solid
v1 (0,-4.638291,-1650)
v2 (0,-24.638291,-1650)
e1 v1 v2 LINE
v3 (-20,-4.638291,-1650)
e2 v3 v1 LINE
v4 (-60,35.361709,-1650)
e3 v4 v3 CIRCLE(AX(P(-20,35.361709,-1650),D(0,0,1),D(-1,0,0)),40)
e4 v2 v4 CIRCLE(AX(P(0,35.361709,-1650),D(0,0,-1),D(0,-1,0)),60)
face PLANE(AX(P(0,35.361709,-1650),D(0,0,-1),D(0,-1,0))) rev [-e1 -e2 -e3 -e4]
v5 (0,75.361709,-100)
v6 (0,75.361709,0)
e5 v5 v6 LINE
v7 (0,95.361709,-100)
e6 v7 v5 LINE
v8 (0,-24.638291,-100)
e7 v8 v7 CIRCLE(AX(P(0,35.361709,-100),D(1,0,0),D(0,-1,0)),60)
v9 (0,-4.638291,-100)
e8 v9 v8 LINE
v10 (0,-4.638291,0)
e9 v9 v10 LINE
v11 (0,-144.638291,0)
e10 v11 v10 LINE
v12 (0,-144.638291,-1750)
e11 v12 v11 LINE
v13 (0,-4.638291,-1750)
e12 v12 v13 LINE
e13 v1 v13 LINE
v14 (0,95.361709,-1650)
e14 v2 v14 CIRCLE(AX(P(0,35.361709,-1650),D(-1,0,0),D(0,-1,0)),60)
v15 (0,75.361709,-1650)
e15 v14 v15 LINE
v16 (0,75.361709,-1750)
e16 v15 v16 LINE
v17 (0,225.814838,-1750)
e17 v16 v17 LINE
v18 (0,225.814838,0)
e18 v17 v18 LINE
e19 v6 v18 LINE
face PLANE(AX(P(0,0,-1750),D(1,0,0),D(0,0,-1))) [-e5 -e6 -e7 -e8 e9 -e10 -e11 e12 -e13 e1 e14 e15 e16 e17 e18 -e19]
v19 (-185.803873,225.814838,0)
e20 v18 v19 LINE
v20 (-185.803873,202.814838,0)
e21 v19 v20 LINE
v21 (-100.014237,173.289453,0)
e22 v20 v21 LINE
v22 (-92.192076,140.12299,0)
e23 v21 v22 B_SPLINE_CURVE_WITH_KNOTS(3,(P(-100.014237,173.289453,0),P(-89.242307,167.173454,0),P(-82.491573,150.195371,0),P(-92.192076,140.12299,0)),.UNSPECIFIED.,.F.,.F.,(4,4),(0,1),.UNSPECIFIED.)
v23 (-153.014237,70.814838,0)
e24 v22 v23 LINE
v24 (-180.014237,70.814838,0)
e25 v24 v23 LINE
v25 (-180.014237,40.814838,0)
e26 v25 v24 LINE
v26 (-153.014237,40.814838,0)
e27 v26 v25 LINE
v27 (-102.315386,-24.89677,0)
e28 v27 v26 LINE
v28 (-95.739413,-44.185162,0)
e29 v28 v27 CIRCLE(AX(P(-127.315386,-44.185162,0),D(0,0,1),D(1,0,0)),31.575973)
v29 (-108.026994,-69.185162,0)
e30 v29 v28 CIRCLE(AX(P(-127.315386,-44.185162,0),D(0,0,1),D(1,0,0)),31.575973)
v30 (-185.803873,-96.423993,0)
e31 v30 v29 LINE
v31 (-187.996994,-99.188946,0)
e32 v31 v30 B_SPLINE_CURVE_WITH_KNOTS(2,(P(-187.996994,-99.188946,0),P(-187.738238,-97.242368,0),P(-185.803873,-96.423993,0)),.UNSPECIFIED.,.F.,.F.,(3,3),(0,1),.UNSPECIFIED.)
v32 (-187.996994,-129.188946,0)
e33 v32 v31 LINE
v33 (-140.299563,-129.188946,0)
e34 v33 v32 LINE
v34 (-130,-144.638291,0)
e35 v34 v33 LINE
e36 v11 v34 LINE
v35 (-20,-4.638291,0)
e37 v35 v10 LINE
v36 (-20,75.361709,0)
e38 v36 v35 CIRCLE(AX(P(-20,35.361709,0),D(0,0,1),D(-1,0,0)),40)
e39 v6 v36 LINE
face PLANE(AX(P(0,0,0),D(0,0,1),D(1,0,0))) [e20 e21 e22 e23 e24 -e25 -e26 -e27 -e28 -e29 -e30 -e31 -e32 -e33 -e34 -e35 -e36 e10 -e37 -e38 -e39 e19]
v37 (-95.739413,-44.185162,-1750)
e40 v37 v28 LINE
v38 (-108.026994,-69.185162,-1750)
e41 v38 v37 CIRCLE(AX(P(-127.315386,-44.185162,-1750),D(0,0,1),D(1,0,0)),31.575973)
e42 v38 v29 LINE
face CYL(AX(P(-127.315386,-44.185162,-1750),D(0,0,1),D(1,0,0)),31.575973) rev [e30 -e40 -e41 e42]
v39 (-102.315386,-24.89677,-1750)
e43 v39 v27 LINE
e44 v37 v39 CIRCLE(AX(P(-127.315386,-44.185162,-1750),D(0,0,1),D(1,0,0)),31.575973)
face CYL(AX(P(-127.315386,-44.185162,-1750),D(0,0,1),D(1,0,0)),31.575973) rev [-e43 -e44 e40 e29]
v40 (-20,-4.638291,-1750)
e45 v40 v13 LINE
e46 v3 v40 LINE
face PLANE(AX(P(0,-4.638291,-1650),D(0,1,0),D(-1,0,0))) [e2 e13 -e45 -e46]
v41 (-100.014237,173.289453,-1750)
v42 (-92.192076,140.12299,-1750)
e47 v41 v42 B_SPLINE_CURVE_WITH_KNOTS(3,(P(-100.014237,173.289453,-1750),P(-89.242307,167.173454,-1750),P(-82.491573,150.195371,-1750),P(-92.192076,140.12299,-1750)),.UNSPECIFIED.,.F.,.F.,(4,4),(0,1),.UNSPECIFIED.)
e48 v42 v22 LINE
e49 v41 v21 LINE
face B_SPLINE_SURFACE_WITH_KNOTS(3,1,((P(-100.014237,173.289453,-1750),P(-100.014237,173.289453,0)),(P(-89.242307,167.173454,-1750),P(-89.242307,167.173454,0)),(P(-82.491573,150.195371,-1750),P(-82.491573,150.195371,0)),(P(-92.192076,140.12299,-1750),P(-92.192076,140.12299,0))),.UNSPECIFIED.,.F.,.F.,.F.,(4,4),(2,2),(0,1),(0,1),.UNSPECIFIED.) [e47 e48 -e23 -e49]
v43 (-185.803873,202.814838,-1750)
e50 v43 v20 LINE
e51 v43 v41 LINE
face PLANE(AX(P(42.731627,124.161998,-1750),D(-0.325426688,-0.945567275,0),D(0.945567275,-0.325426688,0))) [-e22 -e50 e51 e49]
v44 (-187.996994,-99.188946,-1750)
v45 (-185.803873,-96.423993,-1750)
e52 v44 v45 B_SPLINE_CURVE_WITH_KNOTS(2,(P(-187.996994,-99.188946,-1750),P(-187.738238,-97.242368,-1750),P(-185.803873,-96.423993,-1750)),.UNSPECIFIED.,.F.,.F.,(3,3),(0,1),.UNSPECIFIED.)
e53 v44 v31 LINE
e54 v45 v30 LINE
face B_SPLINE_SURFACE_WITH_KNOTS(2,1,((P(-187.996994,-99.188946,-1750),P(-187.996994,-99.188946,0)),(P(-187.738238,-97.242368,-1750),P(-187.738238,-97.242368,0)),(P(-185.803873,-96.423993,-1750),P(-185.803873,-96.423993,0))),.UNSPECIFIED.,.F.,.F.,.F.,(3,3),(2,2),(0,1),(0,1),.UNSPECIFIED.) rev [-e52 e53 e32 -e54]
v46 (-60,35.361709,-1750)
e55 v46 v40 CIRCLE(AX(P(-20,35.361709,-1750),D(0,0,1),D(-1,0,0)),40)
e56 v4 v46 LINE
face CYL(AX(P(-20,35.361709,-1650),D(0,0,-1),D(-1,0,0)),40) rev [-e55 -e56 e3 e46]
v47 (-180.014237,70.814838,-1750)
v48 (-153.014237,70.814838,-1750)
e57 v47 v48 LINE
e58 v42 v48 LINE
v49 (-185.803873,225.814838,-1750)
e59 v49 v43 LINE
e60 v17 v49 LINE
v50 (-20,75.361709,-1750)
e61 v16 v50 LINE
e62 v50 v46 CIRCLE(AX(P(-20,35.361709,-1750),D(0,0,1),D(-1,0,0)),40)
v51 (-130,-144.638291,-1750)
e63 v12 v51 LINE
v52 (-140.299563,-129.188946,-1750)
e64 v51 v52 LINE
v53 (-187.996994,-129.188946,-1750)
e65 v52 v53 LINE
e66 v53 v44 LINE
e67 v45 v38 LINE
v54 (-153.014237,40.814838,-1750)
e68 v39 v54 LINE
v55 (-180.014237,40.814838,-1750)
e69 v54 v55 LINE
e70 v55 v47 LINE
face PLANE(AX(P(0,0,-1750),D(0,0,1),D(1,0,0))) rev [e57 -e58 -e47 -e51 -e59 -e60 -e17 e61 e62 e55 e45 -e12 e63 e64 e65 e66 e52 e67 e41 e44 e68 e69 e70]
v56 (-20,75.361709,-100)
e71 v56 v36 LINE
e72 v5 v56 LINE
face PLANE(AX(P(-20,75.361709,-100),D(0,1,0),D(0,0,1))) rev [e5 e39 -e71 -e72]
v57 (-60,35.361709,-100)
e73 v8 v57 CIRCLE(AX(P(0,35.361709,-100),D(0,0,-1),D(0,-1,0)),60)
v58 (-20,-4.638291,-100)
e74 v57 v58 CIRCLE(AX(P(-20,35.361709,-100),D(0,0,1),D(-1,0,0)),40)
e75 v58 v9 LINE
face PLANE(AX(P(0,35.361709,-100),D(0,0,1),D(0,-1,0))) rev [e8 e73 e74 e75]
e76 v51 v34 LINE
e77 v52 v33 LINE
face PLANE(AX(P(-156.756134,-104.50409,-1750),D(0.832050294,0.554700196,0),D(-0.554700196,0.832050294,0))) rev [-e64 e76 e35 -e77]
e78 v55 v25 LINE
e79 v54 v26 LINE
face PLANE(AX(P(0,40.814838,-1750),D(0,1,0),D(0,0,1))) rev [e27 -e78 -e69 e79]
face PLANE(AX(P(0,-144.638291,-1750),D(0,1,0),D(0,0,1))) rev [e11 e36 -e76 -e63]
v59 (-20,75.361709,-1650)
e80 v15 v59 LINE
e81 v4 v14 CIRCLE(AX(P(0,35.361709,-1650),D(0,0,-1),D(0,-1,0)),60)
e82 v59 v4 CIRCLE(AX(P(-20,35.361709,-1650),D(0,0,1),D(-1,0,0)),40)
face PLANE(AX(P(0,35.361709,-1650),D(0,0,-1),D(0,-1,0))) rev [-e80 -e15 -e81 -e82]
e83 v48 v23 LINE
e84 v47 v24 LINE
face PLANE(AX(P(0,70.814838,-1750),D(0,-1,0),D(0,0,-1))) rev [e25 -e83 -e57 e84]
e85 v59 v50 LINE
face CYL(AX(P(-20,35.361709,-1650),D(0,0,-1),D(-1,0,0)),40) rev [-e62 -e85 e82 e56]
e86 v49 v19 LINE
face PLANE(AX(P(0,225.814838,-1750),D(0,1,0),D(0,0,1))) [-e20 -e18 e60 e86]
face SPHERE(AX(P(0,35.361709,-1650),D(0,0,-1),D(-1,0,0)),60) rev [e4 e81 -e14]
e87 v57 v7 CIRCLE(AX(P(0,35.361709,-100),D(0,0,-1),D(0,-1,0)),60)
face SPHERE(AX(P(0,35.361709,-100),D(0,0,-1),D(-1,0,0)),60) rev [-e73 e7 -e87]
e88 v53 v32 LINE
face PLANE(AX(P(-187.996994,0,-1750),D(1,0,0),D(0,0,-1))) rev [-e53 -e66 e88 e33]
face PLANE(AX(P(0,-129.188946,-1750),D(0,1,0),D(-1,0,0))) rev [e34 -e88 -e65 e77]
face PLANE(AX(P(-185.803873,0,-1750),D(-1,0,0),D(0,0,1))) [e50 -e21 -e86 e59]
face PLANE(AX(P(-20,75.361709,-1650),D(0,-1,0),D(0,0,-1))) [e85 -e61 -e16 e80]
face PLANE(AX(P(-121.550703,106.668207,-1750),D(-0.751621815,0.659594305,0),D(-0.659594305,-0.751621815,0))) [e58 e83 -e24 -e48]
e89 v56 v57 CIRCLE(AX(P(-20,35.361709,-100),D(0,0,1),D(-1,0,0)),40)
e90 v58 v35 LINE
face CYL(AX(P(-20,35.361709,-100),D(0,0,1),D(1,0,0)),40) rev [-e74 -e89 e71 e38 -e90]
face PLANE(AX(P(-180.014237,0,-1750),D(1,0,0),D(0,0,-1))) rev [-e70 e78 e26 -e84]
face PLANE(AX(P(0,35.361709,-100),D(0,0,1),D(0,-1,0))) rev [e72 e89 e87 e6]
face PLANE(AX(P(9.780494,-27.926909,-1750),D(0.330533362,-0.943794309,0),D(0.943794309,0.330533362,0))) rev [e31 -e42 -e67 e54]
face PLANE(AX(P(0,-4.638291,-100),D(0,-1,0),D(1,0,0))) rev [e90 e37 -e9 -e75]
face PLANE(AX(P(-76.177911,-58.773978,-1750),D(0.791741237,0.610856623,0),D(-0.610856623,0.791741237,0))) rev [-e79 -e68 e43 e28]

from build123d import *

# Parameters (mm, degrees)
EXTRUDE_1_DEPTH     = 1750
CUT_EXTRUDE_3_DEPTH = 100
CUT_REVOLVE_1_ANGLE = 90


with BuildPart() as part:
    # 草图1 → 凸台-拉伸1 (new body)
    with BuildSketch(Plane.XY):
        with BuildLine():
            Line((-130, -144.638291086), (0, -144.638291086))
            Line((0, -144.638291086), (0, -4.188946248))
            Line((0, -4.188946248), (0, 75.811053752))
            Line((0, 75.811053752), (0, 185.69710624))
            Line((0, 185.69710624), (0, 225.814837569))
            Line((0, 225.814837569), (-108.083873316, 225.814837569))
            Line((-108.083873316, 225.814837569), (-185.80387332, 225.814837569))
            Line((-185.80387332, 225.814837569), (-185.80387332, 202.814837569))
            Line((-185.80387332, 202.814837569), (-100.01423666, 173.289453092))
            add(Edge.make_bspline(
                [(-100.01423666, 173.289453092), (-89.242307137, 167.173453817), (-82.491572572, 150.19537082), (-92.192076155, 140.122990005)],
                knots=[0, 0, 0, 0, 1, 1, 1, 1], degree=3))
            Line((-92.192076155, 140.122990005), (-153.01423666, 70.814837569))
            Line((-153.01423666, 70.814837569), (-180.01423666, 70.814837569))
            Line((-180.01423666, 70.814837569), (-180.01423666, 40.814837569))
            Line((-180.01423666, 40.814837569), (-153.01423666, 40.814837569))
            Line((-153.01423666, 40.814837569), (-102.31538594, -24.896770131))
            ThreePointArc((-102.31538594, -24.896770131), (-95.998763417, -48.223878967), (-108.02699364, -69.185162431))
            Line((-108.02699364, -69.185162431), (-185.80387332, -96.42399324))
            add(Edge.make_bspline(
                [(-187.99699364, -99.18894625), (-187.738237709, -97.242367883), (-185.80387332, -96.42399324)],
                knots=[0, 0, 0, 1, 1, 1], degree=2))
            Line((-187.99699364, -99.18894625), (-187.99699364, -129.188946248))
            Line((-187.99699364, -129.188946248), (-140.299563226, -129.188946248))
            Line((-140.299563226, -129.188946248), (-130, -144.638291086))
        make_face()
    extrude(amount=-EXTRUDE_1_DEPTH)

    # 草图3 → 切除-拉伸3 (cut)
    with BuildSketch(Plane.XY):
        with BuildLine():
            Line((0, -4.638291086), (-20, -4.638291086))
            ThreePointArc((-20, -4.638291086), (-60, 35.361708914), (-20, 75.361708914))
            Line((-20, 75.361708914), (0, 75.361708914))
            Line((0, 75.361708914), (0, -4.638291086))
        make_face()
    cut_extrude_3 = extrude(amount=-CUT_EXTRUDE_3_DEPTH, mode=Mode.SUBTRACT)

    # 草图5 → 切除-旋转1 (revolve, cut)
    with BuildSketch(Plane(origin=(0, 0, 0), x_dir=(0, 0, -1), z_dir=(1, 0, 0))):
        with BuildLine():
            Line((100, 95.361708914), (100, -24.638291086))
            ThreePointArc((100, -24.638291086), (160, 35.361708914), (100, 95.361708914))
        make_face()
    cut_revolve_1 = revolve(axis=Axis((0, 95.361708914, -100), (0, 1, 0)), revolution_arc=CUT_REVOLVE_1_ANGLE, mode=Mode.SUBTRACT)

    # 镜向1: 切除-拉伸3, 切除-旋转1 across plane
    add(cut_extrude_3.mirror(Plane.XY.offset(-875)), mode=Mode.SUBTRACT)
    add(cut_revolve_1.mirror(Plane.XY.offset(-875)), mode=Mode.SUBTRACT)


solid = part.part
